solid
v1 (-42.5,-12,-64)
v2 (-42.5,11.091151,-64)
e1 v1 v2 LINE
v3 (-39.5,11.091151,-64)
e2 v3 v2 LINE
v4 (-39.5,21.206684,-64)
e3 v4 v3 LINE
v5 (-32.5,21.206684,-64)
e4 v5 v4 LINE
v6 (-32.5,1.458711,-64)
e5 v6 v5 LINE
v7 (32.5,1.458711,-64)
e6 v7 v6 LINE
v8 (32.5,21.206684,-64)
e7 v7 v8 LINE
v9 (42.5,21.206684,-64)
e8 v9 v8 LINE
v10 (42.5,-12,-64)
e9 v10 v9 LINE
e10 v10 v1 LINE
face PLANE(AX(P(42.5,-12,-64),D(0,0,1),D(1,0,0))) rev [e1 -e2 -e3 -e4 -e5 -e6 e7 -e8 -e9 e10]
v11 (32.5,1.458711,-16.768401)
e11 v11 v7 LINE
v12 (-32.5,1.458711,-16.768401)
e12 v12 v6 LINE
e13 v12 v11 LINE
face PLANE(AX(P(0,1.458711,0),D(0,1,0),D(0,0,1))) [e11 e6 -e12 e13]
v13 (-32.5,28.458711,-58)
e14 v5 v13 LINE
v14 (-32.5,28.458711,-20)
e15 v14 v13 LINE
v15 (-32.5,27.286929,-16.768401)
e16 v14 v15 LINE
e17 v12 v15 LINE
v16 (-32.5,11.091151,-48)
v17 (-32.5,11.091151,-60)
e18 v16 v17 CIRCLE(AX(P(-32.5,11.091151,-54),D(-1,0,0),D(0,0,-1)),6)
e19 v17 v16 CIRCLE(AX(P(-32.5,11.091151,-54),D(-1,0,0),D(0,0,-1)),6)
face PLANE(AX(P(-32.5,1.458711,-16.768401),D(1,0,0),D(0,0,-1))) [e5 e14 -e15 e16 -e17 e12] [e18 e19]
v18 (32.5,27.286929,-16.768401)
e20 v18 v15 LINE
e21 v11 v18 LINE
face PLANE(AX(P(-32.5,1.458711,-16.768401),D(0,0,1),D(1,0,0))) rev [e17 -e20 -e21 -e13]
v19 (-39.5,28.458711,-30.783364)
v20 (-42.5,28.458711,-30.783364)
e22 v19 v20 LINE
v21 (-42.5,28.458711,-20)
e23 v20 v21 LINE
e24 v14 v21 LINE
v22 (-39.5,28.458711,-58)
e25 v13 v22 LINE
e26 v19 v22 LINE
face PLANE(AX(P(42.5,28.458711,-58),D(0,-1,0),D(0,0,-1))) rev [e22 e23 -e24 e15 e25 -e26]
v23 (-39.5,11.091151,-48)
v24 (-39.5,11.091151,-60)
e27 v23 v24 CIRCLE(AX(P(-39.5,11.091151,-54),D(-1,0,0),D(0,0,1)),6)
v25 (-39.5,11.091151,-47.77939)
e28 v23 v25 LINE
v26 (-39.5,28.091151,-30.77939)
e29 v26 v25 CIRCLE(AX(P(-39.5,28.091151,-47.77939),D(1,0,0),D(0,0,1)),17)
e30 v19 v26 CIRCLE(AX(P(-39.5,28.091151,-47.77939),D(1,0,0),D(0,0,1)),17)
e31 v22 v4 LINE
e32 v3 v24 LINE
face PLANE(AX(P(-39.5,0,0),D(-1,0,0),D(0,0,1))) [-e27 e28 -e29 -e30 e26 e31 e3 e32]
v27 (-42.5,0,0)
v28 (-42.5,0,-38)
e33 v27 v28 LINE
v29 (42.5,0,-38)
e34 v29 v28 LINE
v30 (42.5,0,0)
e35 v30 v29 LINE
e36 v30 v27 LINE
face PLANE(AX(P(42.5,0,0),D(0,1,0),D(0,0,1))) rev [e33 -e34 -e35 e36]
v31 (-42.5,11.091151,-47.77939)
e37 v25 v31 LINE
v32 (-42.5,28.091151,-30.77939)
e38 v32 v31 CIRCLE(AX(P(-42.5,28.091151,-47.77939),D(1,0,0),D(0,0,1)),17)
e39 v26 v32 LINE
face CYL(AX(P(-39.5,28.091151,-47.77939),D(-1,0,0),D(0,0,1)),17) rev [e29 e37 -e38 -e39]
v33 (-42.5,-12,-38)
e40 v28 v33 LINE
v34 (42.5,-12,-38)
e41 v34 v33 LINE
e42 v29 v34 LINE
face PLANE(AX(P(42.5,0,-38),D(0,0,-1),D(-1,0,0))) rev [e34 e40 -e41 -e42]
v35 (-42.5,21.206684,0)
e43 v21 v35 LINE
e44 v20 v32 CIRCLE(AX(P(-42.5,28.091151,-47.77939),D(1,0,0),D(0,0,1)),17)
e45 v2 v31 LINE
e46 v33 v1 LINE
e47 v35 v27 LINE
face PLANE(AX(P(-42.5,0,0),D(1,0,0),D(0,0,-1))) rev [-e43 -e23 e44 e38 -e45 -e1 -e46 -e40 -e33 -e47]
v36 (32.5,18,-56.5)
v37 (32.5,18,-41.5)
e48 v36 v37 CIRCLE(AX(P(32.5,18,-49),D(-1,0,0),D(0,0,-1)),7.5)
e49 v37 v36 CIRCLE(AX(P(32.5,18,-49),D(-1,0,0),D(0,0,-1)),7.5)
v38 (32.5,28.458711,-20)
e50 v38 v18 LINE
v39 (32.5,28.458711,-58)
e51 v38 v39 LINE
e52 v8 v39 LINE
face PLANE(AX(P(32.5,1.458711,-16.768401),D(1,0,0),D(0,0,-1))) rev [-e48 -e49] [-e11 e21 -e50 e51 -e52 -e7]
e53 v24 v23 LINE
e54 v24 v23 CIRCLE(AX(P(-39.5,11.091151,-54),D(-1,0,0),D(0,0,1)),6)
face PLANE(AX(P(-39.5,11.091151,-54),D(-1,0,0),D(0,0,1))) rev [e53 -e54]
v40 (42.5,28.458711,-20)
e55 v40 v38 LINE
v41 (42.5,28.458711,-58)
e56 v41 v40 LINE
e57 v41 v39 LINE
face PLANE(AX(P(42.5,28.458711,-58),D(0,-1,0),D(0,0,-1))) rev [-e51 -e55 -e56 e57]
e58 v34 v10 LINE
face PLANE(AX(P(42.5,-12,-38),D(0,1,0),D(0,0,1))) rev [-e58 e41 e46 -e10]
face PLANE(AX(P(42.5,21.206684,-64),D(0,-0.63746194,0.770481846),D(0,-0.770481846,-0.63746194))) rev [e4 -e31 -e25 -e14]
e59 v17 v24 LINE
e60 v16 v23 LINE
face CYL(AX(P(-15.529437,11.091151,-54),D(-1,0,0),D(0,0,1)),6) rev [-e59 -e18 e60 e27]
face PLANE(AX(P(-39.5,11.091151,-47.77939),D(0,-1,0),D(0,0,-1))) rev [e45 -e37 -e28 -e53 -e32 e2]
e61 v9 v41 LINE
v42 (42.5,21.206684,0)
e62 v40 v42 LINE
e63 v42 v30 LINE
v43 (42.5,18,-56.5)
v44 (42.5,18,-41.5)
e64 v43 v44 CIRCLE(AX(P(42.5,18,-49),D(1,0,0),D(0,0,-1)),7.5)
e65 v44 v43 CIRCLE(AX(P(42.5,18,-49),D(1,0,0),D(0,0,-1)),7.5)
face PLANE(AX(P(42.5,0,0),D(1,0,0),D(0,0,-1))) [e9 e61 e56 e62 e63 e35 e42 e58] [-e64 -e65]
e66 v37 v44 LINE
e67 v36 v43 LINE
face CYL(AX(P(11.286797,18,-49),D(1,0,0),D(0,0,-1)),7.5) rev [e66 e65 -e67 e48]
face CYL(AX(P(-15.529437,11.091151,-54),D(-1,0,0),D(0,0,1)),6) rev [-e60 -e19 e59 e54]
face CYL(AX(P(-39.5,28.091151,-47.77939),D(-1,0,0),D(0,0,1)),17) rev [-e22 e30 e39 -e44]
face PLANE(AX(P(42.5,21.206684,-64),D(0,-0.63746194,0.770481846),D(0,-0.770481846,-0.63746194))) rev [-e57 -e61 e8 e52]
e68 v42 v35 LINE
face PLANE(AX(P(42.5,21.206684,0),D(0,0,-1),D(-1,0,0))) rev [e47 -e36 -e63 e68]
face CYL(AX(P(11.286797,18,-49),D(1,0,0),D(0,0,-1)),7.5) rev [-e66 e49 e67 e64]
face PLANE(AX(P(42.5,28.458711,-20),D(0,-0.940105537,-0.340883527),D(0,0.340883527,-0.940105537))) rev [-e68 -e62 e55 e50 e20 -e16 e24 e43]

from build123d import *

# Parameters (mm, degrees)
BEARING_BLOCK_DEPTH    = 42.5
LUG_SLOT_PROFILE_W     = 65
LUG_SLOT_PROFILE_H     = 50
LUG_SLOT_65X50_DEPTH   = 27
BORE_15_SKETCH_R       = 7.5
PIVOT_BORE_15_DEPTH    = 10
LUG_RECESS_A_3MM_DEPTH = 3
LUG_RECESS_B_3MM_DEPTH = 3
BORE_10_SKETCH_R       = 6
PIVOT_BORE_10_DEPTH    = 7


with BuildPart() as part:
    # Bearing Block Profile → Bearing Block (new, symmetric)
    with BuildSketch(Plane(origin=(0, 0, 0), x_dir=(0, 0, -1), z_dir=(1, 0, 0))):
        Polygon((0, 0), (38, 0), (38, -12), (64, -12), (64, 21.206684422), (58, 28.458711219), (20, 28.458711219), (0, 21.206684422), align=None)
    extrude(amount=BEARING_BLOCK_DEPTH, both=True)

    # Lug Slot Profile → Lug Slot 65x50 (cut)
    with BuildSketch(Plane(origin=(0, 28.458711219, 0), x_dir=(1, 0, 0), z_dir=(0, 1, 0))):
        with Locations((0, 41.768401258)):
            Rectangle(LUG_SLOT_PROFILE_W, LUG_SLOT_PROFILE_H)
    extrude(amount=-LUG_SLOT_65X50_DEPTH, mode=Mode.SUBTRACT)

    # Bore Ø15 Sketch → Pivot Bore Ø15 (cut)
    with BuildSketch(Plane(origin=(42.5, 0, 0), x_dir=(0, 0, -1), z_dir=(1, 0, 0))):
        with Locations((49, 18)):
            Circle(BORE_15_SKETCH_R)
    extrude(amount=-PIVOT_BORE_15_DEPTH, mode=Mode.SUBTRACT)

    # Lug Recess A Profile → Lug Recess A 3mm (cut)
    with BuildSketch(Plane.ZY.offset(42.5)):
        with BuildLine():
            Line((-58, 28.458711219), (-63.551815655, 21.748391902))
            ThreePointArc((-63.551815655, 21.748391902), (-44.368906721, 11.436763576), (-30.783363951, 28.458711219))
            Line((-30.783363951, 28.458711219), (-58, 28.458711219))
        make_face()
    extrude(amount=-LUG_RECESS_A_3MM_DEPTH, mode=Mode.SUBTRACT)

    # Lug Recess B Profile → Lug Recess B 3mm (cut)
    with BuildSketch(Plane.ZY.offset(42.5)):
        Polygon((-47.779389931, 11.091150514), (-64, 11.091150514), (-64, 21.206684422), (-63.551815655, 21.748391902), align=None)
    extrude(amount=-LUG_RECESS_B_3MM_DEPTH, mode=Mode.SUBTRACT)

    # Bore Ø10 Sketch → Pivot Bore Ø10 (cut)
    with BuildSketch(Plane.ZY.offset(39.5)):
        with Locations(Location((-54, 11.091150514, 0), (0, 0, 180))):
            Circle(BORE_10_SKETCH_R)
    extrude(amount=-PIVOT_BORE_10_DEPTH, mode=Mode.SUBTRACT)


solid = part.part
